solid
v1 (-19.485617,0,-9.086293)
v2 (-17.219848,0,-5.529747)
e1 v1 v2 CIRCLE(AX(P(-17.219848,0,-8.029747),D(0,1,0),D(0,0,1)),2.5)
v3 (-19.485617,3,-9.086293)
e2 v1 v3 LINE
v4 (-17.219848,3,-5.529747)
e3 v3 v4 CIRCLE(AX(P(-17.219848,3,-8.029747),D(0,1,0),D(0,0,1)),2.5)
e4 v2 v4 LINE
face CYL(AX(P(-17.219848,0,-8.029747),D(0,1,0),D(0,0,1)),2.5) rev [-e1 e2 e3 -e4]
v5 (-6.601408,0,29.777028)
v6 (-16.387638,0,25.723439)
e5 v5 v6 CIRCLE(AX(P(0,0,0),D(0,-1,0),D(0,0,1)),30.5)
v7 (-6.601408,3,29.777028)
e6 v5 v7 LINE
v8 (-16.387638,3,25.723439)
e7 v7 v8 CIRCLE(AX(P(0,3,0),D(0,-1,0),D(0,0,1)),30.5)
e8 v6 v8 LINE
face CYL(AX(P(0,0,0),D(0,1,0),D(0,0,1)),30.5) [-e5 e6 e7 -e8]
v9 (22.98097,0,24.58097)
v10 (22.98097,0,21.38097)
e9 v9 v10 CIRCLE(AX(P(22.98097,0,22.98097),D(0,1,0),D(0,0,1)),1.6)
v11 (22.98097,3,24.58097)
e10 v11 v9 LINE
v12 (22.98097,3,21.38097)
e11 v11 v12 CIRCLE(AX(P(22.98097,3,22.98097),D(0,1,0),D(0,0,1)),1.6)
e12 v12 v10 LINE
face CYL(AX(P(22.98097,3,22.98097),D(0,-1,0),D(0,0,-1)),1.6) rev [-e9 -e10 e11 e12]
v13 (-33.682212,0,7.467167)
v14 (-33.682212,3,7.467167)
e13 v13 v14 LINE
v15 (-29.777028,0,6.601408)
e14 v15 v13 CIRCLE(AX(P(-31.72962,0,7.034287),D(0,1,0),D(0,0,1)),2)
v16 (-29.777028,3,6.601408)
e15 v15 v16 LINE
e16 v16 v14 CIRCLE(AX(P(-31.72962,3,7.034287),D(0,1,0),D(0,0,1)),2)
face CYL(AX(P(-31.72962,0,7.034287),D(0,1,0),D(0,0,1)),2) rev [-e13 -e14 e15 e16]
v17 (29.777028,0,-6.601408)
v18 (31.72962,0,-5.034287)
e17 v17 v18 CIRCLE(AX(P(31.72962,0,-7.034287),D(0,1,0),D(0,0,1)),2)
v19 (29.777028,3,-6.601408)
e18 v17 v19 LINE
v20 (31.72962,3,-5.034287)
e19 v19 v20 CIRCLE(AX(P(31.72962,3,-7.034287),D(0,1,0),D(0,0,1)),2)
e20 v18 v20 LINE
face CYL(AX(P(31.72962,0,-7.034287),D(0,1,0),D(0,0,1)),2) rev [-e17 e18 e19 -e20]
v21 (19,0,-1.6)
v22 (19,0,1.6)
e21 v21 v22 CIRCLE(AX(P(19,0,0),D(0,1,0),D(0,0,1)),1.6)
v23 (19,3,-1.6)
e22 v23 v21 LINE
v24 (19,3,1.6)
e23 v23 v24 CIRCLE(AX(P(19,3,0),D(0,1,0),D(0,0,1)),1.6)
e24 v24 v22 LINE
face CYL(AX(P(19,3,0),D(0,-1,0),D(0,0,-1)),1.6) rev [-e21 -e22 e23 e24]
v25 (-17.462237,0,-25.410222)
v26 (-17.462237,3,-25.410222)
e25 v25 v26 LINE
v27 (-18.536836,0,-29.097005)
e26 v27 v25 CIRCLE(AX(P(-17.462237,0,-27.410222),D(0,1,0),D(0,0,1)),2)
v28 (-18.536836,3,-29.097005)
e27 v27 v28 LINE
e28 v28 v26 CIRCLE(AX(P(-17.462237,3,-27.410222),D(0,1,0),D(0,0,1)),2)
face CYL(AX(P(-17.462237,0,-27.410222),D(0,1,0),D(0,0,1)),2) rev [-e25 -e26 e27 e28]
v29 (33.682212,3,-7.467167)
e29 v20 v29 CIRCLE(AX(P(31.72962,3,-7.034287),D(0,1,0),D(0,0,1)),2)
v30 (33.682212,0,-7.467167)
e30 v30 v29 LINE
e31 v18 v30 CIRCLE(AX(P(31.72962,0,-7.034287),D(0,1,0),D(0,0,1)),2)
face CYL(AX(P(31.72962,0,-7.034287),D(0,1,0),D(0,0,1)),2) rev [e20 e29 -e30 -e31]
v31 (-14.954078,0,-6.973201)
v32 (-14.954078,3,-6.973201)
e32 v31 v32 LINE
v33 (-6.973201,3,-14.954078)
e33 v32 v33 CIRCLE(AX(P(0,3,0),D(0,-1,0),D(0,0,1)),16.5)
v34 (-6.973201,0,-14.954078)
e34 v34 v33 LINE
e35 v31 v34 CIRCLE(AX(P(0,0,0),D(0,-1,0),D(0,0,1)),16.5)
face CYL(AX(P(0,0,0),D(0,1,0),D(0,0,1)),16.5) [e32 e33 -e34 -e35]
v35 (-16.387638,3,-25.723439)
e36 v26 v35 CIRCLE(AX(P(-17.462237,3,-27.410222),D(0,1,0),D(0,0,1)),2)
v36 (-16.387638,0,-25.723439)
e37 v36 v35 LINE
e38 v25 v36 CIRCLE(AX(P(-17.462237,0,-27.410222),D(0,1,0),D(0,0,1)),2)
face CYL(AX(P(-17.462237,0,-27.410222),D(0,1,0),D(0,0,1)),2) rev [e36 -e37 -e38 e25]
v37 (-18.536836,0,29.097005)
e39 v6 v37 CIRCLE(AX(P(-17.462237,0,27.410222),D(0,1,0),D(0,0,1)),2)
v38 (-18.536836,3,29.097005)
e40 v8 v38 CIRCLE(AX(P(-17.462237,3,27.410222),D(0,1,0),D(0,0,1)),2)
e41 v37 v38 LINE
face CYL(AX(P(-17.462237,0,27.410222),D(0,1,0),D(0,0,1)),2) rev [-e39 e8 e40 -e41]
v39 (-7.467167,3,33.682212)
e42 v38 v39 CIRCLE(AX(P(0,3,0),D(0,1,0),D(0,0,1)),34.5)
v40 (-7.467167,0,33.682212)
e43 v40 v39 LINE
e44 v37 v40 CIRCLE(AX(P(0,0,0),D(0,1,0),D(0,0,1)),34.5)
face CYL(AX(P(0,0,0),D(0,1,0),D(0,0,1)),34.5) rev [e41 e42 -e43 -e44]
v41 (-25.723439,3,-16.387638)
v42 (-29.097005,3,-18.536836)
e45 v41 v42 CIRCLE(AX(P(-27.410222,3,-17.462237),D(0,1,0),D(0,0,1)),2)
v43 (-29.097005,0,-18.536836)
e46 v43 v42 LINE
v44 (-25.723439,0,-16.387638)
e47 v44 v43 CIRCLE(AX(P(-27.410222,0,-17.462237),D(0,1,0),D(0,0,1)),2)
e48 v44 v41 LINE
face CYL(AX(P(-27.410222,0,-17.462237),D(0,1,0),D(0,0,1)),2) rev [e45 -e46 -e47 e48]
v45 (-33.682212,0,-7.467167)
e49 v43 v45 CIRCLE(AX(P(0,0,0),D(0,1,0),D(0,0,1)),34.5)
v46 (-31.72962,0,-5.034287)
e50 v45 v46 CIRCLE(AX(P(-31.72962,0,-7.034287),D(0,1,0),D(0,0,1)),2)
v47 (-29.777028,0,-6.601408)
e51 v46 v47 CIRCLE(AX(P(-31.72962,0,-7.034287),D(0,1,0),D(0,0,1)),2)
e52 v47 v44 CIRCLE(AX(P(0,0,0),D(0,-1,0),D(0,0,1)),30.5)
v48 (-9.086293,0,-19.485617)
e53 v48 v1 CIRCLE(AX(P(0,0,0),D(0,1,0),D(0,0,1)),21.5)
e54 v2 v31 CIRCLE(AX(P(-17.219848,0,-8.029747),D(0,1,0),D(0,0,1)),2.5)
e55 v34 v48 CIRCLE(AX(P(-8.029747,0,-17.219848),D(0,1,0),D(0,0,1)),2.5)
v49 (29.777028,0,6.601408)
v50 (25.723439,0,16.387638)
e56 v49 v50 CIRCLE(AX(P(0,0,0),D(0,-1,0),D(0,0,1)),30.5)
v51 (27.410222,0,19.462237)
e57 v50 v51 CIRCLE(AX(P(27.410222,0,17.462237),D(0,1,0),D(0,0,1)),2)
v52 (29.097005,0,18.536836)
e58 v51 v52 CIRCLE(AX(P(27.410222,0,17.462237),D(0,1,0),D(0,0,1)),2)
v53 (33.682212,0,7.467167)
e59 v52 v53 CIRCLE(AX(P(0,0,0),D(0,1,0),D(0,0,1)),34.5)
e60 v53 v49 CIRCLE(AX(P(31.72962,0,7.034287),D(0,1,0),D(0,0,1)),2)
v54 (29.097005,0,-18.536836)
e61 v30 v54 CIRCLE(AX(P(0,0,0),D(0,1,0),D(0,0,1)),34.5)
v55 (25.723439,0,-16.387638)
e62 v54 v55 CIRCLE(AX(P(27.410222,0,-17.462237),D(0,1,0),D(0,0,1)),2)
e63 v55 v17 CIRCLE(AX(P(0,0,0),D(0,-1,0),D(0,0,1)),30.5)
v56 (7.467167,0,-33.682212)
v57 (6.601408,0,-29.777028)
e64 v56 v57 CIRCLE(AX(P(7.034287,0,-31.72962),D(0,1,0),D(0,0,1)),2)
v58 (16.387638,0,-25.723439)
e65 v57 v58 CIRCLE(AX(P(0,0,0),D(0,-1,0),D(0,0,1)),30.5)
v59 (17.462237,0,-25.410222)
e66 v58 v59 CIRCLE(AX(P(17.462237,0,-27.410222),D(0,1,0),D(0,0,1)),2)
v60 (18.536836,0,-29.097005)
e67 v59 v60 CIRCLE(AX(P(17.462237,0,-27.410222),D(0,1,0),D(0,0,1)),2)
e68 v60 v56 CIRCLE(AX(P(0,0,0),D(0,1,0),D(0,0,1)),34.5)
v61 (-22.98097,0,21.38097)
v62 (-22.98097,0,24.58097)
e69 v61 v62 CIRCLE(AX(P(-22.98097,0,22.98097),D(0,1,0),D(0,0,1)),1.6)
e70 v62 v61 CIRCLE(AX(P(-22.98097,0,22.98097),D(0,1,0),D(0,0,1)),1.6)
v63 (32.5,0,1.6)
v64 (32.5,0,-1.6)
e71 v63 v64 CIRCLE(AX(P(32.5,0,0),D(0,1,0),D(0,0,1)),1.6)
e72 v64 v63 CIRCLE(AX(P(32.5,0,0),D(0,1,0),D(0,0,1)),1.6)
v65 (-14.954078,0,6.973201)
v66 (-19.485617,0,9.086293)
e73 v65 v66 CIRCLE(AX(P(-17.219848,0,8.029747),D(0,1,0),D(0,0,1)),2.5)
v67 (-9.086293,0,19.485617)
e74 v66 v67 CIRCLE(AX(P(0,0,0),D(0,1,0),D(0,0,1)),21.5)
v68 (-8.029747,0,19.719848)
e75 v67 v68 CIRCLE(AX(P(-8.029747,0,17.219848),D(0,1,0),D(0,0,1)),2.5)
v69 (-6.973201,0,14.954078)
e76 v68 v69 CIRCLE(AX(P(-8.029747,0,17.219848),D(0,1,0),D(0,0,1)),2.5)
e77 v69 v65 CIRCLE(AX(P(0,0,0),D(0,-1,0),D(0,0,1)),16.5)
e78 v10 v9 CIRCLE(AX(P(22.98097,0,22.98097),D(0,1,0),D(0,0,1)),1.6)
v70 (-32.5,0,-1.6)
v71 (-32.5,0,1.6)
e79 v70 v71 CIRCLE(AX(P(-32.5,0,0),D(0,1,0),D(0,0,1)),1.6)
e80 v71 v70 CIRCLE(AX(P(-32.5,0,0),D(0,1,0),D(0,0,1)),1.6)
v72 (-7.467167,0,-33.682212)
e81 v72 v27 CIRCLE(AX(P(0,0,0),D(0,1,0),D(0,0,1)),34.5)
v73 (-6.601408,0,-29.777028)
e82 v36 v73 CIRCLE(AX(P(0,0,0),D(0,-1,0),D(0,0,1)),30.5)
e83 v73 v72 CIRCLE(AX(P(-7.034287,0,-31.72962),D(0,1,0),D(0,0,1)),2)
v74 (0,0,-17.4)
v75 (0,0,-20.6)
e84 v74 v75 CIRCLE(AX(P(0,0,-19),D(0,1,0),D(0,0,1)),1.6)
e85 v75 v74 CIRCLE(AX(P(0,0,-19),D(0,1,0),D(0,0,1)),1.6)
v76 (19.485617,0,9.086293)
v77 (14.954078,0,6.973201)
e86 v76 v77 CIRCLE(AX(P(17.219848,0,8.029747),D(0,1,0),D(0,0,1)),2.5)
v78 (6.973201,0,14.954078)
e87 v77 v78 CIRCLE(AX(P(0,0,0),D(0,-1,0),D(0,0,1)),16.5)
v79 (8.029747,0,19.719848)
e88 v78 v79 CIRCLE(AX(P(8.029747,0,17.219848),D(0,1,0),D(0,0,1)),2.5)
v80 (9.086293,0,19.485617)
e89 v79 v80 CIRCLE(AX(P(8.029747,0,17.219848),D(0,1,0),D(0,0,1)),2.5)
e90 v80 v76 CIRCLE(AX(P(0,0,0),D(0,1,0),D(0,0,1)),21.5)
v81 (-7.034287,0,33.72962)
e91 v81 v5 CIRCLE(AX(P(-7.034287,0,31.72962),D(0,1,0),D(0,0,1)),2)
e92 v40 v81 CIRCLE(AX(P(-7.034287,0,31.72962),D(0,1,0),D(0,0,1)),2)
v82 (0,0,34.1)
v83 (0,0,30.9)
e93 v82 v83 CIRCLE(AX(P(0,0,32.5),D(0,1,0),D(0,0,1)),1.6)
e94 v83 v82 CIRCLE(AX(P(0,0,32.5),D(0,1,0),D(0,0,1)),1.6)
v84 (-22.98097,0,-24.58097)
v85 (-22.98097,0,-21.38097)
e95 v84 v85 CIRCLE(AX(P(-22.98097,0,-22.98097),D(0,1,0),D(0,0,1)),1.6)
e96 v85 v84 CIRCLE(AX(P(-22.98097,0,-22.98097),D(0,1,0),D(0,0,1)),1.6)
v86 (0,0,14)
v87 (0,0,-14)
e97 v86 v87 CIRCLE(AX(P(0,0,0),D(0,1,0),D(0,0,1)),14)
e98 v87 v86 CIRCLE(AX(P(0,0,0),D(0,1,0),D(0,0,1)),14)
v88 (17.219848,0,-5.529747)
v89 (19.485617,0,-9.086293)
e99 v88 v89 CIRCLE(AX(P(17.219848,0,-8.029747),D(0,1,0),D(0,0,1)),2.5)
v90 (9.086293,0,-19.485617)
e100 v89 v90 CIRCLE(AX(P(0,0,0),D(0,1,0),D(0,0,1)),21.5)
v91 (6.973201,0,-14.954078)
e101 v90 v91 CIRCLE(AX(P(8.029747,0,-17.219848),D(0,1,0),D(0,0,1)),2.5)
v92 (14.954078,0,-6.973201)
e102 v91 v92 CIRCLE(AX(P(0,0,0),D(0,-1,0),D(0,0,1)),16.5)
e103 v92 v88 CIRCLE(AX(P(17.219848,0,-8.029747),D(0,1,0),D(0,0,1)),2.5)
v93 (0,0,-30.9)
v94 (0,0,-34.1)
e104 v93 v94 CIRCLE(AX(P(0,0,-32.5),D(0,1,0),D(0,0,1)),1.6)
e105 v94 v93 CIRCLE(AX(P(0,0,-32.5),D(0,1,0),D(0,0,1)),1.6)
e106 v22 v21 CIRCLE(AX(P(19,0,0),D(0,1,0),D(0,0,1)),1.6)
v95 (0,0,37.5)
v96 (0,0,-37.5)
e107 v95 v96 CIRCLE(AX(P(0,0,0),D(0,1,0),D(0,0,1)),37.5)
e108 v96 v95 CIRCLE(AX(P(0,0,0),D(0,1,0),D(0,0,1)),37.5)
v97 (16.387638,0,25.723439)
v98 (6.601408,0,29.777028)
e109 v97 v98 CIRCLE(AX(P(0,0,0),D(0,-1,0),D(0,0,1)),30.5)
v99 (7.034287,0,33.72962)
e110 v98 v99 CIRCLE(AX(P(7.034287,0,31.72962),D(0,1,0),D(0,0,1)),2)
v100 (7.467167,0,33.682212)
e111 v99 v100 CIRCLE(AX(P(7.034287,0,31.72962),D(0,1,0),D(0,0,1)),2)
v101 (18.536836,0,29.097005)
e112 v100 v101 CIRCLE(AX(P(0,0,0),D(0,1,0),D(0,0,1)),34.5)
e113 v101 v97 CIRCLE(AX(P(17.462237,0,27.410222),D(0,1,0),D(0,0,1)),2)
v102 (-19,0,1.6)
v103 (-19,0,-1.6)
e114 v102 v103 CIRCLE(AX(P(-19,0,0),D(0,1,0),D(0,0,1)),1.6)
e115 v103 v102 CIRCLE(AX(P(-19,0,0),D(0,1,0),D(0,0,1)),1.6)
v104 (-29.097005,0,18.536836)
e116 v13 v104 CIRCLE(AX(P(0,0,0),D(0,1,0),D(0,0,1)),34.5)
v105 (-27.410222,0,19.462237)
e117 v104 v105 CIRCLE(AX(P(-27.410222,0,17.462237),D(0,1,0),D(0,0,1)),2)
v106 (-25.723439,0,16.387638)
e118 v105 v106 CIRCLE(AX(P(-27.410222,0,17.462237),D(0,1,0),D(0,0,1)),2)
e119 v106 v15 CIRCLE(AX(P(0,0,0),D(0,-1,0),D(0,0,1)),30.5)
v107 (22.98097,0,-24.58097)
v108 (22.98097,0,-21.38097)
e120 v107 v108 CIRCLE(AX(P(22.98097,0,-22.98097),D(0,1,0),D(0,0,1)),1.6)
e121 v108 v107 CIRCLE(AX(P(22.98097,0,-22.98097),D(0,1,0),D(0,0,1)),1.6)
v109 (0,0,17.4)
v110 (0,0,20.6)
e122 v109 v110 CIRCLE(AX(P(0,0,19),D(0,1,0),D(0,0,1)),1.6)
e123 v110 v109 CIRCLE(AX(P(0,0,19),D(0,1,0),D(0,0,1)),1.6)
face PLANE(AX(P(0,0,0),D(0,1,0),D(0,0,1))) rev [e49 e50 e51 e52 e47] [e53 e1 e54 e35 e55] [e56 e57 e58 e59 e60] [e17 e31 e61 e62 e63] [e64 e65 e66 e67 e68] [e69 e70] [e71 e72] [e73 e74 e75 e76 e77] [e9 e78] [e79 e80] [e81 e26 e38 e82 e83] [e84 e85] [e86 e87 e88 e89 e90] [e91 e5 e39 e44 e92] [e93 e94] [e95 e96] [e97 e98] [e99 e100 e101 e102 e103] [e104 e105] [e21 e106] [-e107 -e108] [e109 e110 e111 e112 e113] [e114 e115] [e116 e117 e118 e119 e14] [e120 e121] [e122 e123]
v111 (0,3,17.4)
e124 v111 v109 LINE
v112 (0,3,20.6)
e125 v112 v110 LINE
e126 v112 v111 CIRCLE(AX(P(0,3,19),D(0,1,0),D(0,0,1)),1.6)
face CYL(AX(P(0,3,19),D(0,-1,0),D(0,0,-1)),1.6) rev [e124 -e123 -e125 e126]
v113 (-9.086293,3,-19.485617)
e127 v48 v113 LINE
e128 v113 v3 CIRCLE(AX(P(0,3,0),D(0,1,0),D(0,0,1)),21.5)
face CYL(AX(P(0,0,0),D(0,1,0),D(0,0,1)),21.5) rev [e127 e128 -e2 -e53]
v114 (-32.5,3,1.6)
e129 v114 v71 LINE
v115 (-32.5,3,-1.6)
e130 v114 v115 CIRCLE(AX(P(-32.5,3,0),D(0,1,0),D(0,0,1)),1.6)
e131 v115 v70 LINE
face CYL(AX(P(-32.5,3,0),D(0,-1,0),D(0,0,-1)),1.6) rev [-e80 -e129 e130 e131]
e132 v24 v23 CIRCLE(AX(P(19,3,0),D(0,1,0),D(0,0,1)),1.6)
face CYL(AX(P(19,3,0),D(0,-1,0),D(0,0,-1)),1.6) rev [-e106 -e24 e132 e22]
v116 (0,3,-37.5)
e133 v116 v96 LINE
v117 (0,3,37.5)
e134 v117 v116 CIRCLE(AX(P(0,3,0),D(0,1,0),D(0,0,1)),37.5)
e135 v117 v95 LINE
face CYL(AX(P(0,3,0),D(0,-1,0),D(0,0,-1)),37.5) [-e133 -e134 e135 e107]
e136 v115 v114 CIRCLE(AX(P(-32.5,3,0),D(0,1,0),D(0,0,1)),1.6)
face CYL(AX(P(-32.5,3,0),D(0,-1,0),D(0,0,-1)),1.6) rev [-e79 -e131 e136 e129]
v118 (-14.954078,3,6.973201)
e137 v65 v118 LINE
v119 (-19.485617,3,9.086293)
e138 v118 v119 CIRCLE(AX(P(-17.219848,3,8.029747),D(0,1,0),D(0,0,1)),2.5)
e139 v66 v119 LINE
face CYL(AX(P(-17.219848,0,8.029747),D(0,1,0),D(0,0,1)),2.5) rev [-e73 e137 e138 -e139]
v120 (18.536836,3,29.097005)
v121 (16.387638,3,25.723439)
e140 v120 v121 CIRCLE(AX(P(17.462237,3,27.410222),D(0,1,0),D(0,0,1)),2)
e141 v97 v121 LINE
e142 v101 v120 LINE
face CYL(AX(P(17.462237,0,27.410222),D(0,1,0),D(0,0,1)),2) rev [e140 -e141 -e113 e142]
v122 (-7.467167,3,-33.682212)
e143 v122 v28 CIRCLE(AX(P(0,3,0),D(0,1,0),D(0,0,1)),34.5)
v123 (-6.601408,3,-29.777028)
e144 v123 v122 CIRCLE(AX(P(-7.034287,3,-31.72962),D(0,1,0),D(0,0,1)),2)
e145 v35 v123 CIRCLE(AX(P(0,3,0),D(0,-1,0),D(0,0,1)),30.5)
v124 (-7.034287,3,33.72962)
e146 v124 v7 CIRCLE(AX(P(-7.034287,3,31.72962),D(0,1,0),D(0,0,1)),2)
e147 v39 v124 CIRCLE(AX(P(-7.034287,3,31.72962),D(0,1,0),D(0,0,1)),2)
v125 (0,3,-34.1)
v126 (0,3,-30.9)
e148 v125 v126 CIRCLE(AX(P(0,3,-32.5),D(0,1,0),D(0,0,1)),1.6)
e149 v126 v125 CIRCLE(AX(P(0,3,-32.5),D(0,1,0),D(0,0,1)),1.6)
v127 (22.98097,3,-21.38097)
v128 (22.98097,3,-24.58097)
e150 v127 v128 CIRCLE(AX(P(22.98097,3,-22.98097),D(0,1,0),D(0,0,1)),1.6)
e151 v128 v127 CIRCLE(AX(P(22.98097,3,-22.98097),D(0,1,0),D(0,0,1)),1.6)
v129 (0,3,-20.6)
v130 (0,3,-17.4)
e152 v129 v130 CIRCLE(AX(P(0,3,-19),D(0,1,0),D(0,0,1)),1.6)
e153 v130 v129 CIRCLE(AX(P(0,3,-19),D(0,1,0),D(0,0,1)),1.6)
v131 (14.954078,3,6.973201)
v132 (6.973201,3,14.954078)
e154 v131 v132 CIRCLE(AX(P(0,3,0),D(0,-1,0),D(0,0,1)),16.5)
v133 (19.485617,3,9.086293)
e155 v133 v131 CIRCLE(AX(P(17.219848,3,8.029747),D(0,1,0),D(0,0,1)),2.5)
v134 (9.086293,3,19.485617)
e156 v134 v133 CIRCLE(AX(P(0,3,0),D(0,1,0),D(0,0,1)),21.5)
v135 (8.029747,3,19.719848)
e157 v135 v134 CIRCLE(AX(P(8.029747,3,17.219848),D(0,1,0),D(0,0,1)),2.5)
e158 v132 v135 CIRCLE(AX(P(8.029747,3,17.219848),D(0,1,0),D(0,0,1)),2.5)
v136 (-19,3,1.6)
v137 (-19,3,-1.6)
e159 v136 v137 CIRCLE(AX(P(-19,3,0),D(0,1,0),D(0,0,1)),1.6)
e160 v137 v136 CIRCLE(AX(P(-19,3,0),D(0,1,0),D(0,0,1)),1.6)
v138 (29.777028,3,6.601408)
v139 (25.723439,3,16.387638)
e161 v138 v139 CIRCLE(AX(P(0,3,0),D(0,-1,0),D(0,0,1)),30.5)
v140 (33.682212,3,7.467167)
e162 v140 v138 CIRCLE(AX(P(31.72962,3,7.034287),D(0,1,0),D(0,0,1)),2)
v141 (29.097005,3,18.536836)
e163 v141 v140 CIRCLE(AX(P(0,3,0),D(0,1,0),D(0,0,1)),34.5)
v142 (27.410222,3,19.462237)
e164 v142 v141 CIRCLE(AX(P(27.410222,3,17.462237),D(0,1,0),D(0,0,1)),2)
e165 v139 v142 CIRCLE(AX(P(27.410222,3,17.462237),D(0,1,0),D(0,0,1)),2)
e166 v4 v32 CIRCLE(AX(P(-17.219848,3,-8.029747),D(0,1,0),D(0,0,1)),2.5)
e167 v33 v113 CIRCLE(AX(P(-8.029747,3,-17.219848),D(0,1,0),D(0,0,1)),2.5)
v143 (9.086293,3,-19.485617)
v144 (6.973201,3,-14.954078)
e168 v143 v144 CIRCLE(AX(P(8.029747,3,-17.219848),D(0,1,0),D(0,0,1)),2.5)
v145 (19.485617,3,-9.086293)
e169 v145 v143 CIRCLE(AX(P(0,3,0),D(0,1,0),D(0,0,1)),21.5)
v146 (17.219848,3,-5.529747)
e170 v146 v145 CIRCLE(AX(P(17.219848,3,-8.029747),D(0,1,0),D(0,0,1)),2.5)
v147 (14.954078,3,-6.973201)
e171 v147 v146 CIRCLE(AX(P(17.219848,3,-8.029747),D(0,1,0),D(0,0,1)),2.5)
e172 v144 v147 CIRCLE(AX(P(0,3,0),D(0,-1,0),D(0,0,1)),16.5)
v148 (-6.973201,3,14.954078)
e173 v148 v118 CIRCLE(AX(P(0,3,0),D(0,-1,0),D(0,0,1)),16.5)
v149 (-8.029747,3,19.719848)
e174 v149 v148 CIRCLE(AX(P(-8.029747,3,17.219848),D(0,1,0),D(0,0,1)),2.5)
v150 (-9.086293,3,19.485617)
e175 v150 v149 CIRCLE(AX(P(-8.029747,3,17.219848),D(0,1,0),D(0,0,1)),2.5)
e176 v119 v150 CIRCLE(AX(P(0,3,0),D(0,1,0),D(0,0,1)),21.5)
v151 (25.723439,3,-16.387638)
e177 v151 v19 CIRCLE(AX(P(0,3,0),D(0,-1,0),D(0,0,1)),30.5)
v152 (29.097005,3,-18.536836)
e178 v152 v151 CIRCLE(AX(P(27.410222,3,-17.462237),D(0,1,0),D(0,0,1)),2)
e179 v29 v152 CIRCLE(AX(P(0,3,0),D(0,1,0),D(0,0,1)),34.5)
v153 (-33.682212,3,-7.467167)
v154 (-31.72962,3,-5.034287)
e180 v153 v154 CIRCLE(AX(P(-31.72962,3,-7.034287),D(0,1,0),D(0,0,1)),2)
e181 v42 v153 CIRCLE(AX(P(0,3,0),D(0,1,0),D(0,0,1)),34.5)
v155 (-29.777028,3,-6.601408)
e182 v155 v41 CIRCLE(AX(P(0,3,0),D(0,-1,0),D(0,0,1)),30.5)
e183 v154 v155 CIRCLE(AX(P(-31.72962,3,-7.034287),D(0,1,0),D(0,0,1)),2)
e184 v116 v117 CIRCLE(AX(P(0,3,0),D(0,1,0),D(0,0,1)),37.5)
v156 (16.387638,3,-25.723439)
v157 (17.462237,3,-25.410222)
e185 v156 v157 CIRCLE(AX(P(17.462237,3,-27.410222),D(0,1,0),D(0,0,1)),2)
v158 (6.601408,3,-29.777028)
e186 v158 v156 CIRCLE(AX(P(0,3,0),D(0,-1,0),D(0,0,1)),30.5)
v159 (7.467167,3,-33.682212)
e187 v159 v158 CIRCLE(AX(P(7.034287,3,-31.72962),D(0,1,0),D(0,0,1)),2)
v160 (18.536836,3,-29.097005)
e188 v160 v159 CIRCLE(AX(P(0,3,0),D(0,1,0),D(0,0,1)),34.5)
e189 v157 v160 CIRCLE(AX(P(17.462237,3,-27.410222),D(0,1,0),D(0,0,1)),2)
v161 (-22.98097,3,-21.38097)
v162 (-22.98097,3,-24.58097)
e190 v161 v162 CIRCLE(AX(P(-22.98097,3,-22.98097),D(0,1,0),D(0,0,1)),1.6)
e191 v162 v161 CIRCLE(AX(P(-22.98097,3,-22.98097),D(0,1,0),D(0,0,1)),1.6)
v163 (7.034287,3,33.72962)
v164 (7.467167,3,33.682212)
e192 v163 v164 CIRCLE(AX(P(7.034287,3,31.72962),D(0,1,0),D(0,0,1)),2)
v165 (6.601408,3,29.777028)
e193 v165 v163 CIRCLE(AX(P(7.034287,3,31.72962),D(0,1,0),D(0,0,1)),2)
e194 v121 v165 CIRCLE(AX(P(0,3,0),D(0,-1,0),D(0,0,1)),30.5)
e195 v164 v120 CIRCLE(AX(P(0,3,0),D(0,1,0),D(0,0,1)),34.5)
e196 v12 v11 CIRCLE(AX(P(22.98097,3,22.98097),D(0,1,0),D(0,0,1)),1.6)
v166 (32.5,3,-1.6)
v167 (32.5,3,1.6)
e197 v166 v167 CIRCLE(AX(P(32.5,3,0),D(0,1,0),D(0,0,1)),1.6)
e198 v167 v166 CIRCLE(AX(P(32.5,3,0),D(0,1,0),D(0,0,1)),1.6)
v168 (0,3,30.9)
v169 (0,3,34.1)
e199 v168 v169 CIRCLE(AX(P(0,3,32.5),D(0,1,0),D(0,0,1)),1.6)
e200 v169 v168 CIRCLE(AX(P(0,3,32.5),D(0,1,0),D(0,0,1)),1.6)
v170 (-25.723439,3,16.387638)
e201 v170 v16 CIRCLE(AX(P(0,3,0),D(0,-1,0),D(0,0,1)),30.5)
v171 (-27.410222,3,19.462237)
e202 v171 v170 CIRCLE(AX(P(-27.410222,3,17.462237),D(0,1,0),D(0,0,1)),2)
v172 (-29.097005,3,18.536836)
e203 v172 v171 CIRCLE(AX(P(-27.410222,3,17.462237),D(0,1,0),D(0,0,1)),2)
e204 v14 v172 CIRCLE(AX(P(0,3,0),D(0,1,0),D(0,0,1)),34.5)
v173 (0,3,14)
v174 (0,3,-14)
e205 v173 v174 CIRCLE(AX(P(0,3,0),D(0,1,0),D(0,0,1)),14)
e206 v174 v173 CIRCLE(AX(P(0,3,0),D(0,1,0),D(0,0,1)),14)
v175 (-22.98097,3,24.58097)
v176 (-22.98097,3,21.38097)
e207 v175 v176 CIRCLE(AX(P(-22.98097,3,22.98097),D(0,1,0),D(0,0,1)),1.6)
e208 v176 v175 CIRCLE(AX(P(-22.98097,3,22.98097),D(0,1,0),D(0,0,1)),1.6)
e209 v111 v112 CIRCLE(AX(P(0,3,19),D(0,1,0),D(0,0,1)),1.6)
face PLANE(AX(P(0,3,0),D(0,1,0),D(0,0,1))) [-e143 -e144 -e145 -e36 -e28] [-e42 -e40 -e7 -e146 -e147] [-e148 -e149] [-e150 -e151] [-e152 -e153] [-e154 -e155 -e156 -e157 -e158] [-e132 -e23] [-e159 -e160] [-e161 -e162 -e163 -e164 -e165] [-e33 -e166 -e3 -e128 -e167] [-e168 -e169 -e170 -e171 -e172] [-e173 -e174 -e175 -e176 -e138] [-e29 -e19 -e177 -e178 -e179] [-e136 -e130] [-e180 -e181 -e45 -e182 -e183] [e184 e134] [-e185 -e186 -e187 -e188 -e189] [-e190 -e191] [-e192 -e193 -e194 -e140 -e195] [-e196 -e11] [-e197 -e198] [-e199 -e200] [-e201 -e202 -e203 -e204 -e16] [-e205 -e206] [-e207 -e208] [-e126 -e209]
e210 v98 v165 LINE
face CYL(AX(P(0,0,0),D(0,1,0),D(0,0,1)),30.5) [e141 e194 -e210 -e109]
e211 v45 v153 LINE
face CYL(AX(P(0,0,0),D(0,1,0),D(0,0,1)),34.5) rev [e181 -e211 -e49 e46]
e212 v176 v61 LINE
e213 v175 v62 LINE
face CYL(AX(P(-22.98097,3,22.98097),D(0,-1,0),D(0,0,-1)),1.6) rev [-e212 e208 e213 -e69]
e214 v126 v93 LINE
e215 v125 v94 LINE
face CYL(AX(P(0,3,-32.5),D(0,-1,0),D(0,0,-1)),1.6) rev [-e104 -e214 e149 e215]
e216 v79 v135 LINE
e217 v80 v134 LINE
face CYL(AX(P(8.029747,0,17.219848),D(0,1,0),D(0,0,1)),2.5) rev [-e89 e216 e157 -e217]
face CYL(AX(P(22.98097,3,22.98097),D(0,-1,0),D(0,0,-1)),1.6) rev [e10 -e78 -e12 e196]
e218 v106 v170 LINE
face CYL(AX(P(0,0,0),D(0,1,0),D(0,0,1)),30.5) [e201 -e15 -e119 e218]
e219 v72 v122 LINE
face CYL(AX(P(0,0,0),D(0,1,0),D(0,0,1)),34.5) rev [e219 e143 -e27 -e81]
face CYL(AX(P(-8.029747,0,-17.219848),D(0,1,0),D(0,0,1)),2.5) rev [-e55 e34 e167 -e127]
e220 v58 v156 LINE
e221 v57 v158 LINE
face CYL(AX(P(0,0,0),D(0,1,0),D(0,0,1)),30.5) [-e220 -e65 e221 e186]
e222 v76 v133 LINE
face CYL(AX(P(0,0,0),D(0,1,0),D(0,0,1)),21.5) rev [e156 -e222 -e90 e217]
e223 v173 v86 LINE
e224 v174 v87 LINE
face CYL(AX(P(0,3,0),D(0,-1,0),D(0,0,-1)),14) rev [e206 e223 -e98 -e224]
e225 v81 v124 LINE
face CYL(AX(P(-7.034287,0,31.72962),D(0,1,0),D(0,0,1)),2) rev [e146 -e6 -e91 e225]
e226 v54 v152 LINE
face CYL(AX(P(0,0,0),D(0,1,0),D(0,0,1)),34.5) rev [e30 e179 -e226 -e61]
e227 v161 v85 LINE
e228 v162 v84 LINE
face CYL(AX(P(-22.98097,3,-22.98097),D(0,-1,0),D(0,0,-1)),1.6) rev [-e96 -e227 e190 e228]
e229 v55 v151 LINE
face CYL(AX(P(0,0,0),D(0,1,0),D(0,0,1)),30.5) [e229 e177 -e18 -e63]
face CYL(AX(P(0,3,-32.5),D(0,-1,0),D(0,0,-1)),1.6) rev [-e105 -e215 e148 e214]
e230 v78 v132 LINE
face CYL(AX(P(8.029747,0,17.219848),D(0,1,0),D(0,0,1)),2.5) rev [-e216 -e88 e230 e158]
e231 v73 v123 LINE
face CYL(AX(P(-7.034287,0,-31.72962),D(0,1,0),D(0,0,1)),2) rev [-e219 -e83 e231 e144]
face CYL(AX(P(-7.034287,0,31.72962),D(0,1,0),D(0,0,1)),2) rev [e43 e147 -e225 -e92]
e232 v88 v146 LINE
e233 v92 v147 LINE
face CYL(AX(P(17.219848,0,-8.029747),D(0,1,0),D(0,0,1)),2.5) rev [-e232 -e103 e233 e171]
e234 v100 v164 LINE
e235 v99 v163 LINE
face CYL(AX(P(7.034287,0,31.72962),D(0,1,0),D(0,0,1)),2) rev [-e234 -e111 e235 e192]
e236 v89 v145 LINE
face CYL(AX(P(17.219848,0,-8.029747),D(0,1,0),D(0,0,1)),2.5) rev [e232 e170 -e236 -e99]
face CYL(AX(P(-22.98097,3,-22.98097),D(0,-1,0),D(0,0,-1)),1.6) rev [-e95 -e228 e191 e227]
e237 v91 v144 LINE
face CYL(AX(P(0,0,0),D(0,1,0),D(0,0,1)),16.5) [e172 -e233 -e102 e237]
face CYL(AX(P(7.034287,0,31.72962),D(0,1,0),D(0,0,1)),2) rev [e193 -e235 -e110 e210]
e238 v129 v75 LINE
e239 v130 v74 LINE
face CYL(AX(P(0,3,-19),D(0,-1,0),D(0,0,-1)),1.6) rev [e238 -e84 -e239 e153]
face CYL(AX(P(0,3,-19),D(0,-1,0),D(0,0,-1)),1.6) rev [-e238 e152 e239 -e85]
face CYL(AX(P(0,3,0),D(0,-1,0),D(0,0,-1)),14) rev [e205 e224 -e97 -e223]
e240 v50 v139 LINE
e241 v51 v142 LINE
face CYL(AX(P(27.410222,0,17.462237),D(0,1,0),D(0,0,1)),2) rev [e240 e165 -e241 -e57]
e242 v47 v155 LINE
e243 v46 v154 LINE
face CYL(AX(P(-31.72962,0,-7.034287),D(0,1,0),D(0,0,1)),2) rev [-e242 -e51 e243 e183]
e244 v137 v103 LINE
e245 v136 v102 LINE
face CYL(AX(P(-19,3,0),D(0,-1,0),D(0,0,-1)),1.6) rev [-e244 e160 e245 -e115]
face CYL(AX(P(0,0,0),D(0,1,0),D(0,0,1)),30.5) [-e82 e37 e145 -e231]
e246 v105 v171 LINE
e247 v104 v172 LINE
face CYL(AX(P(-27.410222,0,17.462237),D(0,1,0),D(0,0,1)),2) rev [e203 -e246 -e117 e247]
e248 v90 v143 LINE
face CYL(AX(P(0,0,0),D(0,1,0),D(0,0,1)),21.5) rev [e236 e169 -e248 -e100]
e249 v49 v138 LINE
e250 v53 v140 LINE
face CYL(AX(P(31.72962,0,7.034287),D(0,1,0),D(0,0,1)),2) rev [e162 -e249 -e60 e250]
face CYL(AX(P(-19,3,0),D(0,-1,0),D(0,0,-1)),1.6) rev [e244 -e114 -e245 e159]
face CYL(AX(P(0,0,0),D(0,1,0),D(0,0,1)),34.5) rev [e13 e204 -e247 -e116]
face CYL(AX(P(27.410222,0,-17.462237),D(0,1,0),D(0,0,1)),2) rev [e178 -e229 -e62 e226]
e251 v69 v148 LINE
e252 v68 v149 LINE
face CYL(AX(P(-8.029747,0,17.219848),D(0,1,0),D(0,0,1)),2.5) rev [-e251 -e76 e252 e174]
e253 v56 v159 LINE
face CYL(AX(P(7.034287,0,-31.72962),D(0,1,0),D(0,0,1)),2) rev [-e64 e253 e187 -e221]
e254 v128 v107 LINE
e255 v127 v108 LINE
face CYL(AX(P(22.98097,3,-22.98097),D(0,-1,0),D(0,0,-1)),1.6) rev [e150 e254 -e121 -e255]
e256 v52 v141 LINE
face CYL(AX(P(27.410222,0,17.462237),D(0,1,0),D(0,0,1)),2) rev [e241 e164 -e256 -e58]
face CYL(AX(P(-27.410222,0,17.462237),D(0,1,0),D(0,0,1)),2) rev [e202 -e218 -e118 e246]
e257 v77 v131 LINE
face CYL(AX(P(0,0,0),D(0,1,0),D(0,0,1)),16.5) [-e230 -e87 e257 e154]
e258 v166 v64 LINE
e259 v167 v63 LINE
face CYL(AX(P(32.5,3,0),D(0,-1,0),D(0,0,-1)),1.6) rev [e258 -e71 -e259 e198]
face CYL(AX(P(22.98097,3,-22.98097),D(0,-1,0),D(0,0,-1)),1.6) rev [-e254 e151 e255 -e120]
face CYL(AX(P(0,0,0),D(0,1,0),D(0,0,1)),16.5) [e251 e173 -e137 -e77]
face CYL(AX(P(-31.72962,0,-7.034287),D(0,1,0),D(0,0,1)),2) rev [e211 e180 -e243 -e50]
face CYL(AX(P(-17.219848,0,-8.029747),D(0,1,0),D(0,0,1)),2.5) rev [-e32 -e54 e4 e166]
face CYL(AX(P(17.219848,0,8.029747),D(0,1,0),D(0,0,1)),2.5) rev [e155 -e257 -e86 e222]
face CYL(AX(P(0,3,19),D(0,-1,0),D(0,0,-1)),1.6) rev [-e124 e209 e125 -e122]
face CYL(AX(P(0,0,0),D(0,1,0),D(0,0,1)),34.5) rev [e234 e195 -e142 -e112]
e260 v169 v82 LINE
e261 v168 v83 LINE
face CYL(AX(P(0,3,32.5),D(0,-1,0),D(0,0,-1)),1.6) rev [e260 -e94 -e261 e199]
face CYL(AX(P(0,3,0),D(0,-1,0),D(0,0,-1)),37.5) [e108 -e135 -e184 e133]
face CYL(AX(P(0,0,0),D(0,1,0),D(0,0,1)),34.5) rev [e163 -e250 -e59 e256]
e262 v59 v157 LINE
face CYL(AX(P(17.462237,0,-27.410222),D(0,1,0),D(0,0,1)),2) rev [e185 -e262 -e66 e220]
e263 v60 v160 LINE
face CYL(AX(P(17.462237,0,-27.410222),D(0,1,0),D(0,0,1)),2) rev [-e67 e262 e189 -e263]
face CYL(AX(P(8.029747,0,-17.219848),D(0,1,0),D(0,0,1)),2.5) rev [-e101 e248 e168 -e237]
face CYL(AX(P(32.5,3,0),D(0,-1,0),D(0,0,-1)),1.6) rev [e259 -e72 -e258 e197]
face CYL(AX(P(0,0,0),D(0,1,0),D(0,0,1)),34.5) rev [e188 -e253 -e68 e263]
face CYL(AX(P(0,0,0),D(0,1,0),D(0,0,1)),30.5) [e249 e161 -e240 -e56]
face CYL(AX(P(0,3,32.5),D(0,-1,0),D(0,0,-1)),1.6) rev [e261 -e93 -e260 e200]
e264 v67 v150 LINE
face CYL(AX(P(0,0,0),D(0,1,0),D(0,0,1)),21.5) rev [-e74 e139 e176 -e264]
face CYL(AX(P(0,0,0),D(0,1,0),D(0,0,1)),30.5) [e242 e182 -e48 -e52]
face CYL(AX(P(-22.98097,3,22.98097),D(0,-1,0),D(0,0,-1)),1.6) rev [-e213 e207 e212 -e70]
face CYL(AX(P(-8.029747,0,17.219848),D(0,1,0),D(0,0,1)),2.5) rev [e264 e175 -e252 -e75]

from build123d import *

# Parameters (mm, degrees)
SKETCH_1_R               = 37.5
SKETCH_1_R_2             = 1.6
SKETCH_1_R_3             = 14
EXTRUDE_1_DEPTH          = 3
CUT_EXTRUDE_1_DEPTH      = 54.117793629
CUT_EXTRUDE_1_DEPTH_BACK = 54.117793629


with BuildPart() as part:
    # 草图1 → 凸台-拉伸1 (new body)
    with BuildSketch(Plane(origin=(0, 0, 0), x_dir=(1, 0, 0), z_dir=(0, 1, 0))):
        with Locations(Location((0, 0, 0), (0, 0, 270))):
            Circle(SKETCH_1_R)
        with Locations(Location((0, 19, 0), (0, 0, 270))):
            Circle(SKETCH_1_R_2, mode=Mode.SUBTRACT)
        with Locations(Location((19, 0, 0), (0, 0, 270))):
            Circle(SKETCH_1_R_2, mode=Mode.SUBTRACT)
        with Locations(Location((0, -19, 0), (0, 0, 270))):
            Circle(SKETCH_1_R_2, mode=Mode.SUBTRACT)
        with Locations(Location((-19, 0, 0), (0, 0, 270))):
            Circle(SKETCH_1_R_2, mode=Mode.SUBTRACT)
        with Locations(Location((0, 32.5, 0), (0, 0, 270))):
            Circle(SKETCH_1_R_2, mode=Mode.SUBTRACT)
        with Locations(Location((22.980970389, 22.980970389, 0), (0, 0, 270))):
            Circle(SKETCH_1_R_2, mode=Mode.SUBTRACT)
        with Locations(Location((32.5, 0, 0), (0, 0, 270))):
            Circle(SKETCH_1_R_2, mode=Mode.SUBTRACT)
        with Locations(Location((22.980970389, -22.980970389, 0), (0, 0, 270))):
            Circle(SKETCH_1_R_2, mode=Mode.SUBTRACT)
        with Locations(Location((0, -32.5, 0), (0, 0, 270))):
            Circle(SKETCH_1_R_2, mode=Mode.SUBTRACT)
        with Locations(Location((-22.980970389, -22.980970389, 0), (0, 0, 270))):
            Circle(SKETCH_1_R_2, mode=Mode.SUBTRACT)
        with Locations(Location((-32.5, 0, 0), (0, 0, 270))):
            Circle(SKETCH_1_R_2, mode=Mode.SUBTRACT)
        with Locations(Location((-22.980970389, 22.980970389, 0), (0, 0, 270))):
            Circle(SKETCH_1_R_2, mode=Mode.SUBTRACT)
        with Locations(Location((0, 0, 0), (0, 0, 270))):
            Circle(SKETCH_1_R_3, mode=Mode.SUBTRACT)
    extrude(amount=EXTRUDE_1_DEPTH)

    # 草图2 → 切除-拉伸1 (cut, two sides: drawn at the far end of the back side and taken through both)
    with BuildSketch(Plane(origin=(0, 3, 0), x_dir=(1, 0, 0), z_dir=(0, 1, 0)).offset(-CUT_EXTRUDE_1_DEPTH_BACK)):
        with BuildLine():
            ThreePointArc((-7.467166681, 33.682212246), (-13.202578417, 31.873843872), (-18.536836488, 29.097004881))
            ThreePointArc((-18.536836488, 29.097004881), (-19.149020163, 26.335622772), (-16.387638055, 25.723439097))
            ThreePointArc((-16.387638055, 25.723439097), (-11.671844687, 28.178325742), (-6.601408225, 29.777028217))
            ThreePointArc((-6.601408225, 29.777028217), (-5.081695439, 32.162499459), (-7.467166681, 33.682212246))
        make_face()
        with BuildLine():
            ThreePointArc((-9.086292627, 19.485617421), (-15.202795796, 15.202795796), (-19.485617421, 9.086292627))
            ThreePointArc((-19.485617421, 9.086292627), (-18.276393608, 5.763977505), (-14.954078486, 6.973201319))
            ThreePointArc((-14.954078486, 6.973201319), (-11.66726189, 11.66726189), (-6.973201319, 14.954078486))
            ThreePointArc((-6.973201319, 14.954078486), (-5.763977505, 18.276393608), (-9.086292627, 19.485617421))
        make_face()
        with BuildLine():
            ThreePointArc((18.536836488, 29.097004881), (13.202578417, 31.873843872), (7.467166681, 33.682212246))
            ThreePointArc((7.467166681, 33.682212246), (5.081695439, 32.162499459), (6.601408225, 29.777028217))
            ThreePointArc((6.601408225, 29.777028217), (11.671844687, 28.178325742), (16.387638055, 25.723439097))
            ThreePointArc((16.387638055, 25.723439097), (19.149020163, 26.335622772), (18.536836488, 29.097004881))
        make_face()
        with BuildLine():
            ThreePointArc((33.682212246, 7.467166681), (31.873843872, 13.202578417), (29.097004881, 18.536836488))
            ThreePointArc((29.097004881, 18.536836488), (26.335622772, 19.149020163), (25.723439097, 16.387638055))
            ThreePointArc((25.723439097, 16.387638055), (28.178325742, 11.671844687), (29.777028217, 6.601408225))
            ThreePointArc((29.777028217, 6.601408225), (32.162499459, 5.081695439), (33.682212246, 7.467166681))
        make_face()
        with BuildLine():
            ThreePointArc((29.097004881, -18.536836488), (31.873843872, -13.202578417), (33.682212246, -7.467166681))
            ThreePointArc((33.682212246, -7.467166681), (32.162499459, -5.081695439), (29.777028217, -6.601408225))
            ThreePointArc((29.777028217, -6.601408225), (28.178325742, -11.671844687), (25.723439097, -16.387638055))
            ThreePointArc((25.723439097, -16.387638055), (26.335622772, -19.149020163), (29.097004881, -18.536836488))
        make_face()
        with BuildLine():
            ThreePointArc((7.467166681, -33.682212246), (13.202578417, -31.873843872), (18.536836488, -29.097004881))
            ThreePointArc((18.536836488, -29.097004881), (19.149020163, -26.335622772), (16.387638055, -25.723439097))
            ThreePointArc((16.387638055, -25.723439097), (11.671844687, -28.178325742), (6.601408225, -29.777028217))
            ThreePointArc((6.601408225, -29.777028217), (5.081695439, -32.162499459), (7.467166681, -33.682212246))
        make_face()
        with BuildLine():
            ThreePointArc((-18.536836488, -29.097004881), (-13.202578417, -31.873843872), (-7.467166681, -33.682212246))
            ThreePointArc((-7.467166681, -33.682212246), (-5.081695439, -32.162499459), (-6.601408225, -29.777028217))
            ThreePointArc((-6.601408225, -29.777028217), (-11.671844687, -28.178325742), (-16.387638055, -25.723439097))
            ThreePointArc((-16.387638055, -25.723439097), (-19.149020163, -26.335622772), (-18.536836488, -29.097004881))
        make_face()
        with BuildLine():
            ThreePointArc((-33.682212246, -7.467166681), (-31.873843872, -13.202578417), (-29.097004881, -18.536836488))
            ThreePointArc((-29.097004881, -18.536836488), (-26.335622772, -19.149020163), (-25.723439097, -16.387638055))
            ThreePointArc((-25.723439097, -16.387638055), (-28.178325742, -11.671844687), (-29.777028217, -6.601408225))
            ThreePointArc((-29.777028217, -6.601408225), (-32.162499459, -5.081695439), (-33.682212246, -7.467166681))
        make_face()
        with BuildLine():
            ThreePointArc((-29.097004881, 18.536836488), (-31.873843872, 13.202578417), (-33.682212246, 7.467166681))
            ThreePointArc((-33.682212246, 7.467166681), (-32.162499459, 5.081695439), (-29.777028217, 6.601408225))
            ThreePointArc((-29.777028217, 6.601408225), (-28.178325742, 11.671844687), (-25.723439097, 16.387638055))
            ThreePointArc((-25.723439097, 16.387638055), (-26.335622772, 19.149020163), (-29.097004881, 18.536836488))
        make_face()
        with BuildLine():
            ThreePointArc((19.485617421, 9.086292627), (15.202795796, 15.202795796), (9.086292627, 19.485617421))
            ThreePointArc((9.086292627, 19.485617421), (5.763977505, 18.276393608), (6.973201319, 14.954078486))
            ThreePointArc((6.973201319, 14.954078486), (11.66726189, 11.66726189), (14.954078486, 6.973201319))
            ThreePointArc((14.954078486, 6.973201319), (18.276393608, 5.763977505), (19.485617421, 9.086292627))
        make_face()
        with BuildLine():
            ThreePointArc((9.086292627, -19.485617421), (15.202795796, -15.202795796), (19.485617421, -9.086292627))
            ThreePointArc((19.485617421, -9.086292627), (18.276393608, -5.763977505), (14.954078486, -6.973201319))
            ThreePointArc((14.954078486, -6.973201319), (11.66726189, -11.66726189), (6.973201319, -14.954078486))
            ThreePointArc((6.973201319, -14.954078486), (5.763977505, -18.276393608), (9.086292627, -19.485617421))
        make_face()
        with BuildLine():
            ThreePointArc((-19.485617421, -9.086292627), (-15.202795796, -15.202795796), (-9.086292627, -19.485617421))
            ThreePointArc((-9.086292627, -19.485617421), (-5.763977505, -18.276393608), (-6.973201319, -14.954078486))
            ThreePointArc((-6.973201319, -14.954078486), (-11.66726189, -11.66726189), (-14.954078486, -6.973201319))
            ThreePointArc((-14.954078486, -6.973201319), (-18.276393608, -5.763977505), (-19.485617421, -9.086292627))
        make_face()
    extrude(amount=CUT_EXTRUDE_1_DEPTH + CUT_EXTRUDE_1_DEPTH_BACK, mode=Mode.SUBTRACT)


solid = part.part
